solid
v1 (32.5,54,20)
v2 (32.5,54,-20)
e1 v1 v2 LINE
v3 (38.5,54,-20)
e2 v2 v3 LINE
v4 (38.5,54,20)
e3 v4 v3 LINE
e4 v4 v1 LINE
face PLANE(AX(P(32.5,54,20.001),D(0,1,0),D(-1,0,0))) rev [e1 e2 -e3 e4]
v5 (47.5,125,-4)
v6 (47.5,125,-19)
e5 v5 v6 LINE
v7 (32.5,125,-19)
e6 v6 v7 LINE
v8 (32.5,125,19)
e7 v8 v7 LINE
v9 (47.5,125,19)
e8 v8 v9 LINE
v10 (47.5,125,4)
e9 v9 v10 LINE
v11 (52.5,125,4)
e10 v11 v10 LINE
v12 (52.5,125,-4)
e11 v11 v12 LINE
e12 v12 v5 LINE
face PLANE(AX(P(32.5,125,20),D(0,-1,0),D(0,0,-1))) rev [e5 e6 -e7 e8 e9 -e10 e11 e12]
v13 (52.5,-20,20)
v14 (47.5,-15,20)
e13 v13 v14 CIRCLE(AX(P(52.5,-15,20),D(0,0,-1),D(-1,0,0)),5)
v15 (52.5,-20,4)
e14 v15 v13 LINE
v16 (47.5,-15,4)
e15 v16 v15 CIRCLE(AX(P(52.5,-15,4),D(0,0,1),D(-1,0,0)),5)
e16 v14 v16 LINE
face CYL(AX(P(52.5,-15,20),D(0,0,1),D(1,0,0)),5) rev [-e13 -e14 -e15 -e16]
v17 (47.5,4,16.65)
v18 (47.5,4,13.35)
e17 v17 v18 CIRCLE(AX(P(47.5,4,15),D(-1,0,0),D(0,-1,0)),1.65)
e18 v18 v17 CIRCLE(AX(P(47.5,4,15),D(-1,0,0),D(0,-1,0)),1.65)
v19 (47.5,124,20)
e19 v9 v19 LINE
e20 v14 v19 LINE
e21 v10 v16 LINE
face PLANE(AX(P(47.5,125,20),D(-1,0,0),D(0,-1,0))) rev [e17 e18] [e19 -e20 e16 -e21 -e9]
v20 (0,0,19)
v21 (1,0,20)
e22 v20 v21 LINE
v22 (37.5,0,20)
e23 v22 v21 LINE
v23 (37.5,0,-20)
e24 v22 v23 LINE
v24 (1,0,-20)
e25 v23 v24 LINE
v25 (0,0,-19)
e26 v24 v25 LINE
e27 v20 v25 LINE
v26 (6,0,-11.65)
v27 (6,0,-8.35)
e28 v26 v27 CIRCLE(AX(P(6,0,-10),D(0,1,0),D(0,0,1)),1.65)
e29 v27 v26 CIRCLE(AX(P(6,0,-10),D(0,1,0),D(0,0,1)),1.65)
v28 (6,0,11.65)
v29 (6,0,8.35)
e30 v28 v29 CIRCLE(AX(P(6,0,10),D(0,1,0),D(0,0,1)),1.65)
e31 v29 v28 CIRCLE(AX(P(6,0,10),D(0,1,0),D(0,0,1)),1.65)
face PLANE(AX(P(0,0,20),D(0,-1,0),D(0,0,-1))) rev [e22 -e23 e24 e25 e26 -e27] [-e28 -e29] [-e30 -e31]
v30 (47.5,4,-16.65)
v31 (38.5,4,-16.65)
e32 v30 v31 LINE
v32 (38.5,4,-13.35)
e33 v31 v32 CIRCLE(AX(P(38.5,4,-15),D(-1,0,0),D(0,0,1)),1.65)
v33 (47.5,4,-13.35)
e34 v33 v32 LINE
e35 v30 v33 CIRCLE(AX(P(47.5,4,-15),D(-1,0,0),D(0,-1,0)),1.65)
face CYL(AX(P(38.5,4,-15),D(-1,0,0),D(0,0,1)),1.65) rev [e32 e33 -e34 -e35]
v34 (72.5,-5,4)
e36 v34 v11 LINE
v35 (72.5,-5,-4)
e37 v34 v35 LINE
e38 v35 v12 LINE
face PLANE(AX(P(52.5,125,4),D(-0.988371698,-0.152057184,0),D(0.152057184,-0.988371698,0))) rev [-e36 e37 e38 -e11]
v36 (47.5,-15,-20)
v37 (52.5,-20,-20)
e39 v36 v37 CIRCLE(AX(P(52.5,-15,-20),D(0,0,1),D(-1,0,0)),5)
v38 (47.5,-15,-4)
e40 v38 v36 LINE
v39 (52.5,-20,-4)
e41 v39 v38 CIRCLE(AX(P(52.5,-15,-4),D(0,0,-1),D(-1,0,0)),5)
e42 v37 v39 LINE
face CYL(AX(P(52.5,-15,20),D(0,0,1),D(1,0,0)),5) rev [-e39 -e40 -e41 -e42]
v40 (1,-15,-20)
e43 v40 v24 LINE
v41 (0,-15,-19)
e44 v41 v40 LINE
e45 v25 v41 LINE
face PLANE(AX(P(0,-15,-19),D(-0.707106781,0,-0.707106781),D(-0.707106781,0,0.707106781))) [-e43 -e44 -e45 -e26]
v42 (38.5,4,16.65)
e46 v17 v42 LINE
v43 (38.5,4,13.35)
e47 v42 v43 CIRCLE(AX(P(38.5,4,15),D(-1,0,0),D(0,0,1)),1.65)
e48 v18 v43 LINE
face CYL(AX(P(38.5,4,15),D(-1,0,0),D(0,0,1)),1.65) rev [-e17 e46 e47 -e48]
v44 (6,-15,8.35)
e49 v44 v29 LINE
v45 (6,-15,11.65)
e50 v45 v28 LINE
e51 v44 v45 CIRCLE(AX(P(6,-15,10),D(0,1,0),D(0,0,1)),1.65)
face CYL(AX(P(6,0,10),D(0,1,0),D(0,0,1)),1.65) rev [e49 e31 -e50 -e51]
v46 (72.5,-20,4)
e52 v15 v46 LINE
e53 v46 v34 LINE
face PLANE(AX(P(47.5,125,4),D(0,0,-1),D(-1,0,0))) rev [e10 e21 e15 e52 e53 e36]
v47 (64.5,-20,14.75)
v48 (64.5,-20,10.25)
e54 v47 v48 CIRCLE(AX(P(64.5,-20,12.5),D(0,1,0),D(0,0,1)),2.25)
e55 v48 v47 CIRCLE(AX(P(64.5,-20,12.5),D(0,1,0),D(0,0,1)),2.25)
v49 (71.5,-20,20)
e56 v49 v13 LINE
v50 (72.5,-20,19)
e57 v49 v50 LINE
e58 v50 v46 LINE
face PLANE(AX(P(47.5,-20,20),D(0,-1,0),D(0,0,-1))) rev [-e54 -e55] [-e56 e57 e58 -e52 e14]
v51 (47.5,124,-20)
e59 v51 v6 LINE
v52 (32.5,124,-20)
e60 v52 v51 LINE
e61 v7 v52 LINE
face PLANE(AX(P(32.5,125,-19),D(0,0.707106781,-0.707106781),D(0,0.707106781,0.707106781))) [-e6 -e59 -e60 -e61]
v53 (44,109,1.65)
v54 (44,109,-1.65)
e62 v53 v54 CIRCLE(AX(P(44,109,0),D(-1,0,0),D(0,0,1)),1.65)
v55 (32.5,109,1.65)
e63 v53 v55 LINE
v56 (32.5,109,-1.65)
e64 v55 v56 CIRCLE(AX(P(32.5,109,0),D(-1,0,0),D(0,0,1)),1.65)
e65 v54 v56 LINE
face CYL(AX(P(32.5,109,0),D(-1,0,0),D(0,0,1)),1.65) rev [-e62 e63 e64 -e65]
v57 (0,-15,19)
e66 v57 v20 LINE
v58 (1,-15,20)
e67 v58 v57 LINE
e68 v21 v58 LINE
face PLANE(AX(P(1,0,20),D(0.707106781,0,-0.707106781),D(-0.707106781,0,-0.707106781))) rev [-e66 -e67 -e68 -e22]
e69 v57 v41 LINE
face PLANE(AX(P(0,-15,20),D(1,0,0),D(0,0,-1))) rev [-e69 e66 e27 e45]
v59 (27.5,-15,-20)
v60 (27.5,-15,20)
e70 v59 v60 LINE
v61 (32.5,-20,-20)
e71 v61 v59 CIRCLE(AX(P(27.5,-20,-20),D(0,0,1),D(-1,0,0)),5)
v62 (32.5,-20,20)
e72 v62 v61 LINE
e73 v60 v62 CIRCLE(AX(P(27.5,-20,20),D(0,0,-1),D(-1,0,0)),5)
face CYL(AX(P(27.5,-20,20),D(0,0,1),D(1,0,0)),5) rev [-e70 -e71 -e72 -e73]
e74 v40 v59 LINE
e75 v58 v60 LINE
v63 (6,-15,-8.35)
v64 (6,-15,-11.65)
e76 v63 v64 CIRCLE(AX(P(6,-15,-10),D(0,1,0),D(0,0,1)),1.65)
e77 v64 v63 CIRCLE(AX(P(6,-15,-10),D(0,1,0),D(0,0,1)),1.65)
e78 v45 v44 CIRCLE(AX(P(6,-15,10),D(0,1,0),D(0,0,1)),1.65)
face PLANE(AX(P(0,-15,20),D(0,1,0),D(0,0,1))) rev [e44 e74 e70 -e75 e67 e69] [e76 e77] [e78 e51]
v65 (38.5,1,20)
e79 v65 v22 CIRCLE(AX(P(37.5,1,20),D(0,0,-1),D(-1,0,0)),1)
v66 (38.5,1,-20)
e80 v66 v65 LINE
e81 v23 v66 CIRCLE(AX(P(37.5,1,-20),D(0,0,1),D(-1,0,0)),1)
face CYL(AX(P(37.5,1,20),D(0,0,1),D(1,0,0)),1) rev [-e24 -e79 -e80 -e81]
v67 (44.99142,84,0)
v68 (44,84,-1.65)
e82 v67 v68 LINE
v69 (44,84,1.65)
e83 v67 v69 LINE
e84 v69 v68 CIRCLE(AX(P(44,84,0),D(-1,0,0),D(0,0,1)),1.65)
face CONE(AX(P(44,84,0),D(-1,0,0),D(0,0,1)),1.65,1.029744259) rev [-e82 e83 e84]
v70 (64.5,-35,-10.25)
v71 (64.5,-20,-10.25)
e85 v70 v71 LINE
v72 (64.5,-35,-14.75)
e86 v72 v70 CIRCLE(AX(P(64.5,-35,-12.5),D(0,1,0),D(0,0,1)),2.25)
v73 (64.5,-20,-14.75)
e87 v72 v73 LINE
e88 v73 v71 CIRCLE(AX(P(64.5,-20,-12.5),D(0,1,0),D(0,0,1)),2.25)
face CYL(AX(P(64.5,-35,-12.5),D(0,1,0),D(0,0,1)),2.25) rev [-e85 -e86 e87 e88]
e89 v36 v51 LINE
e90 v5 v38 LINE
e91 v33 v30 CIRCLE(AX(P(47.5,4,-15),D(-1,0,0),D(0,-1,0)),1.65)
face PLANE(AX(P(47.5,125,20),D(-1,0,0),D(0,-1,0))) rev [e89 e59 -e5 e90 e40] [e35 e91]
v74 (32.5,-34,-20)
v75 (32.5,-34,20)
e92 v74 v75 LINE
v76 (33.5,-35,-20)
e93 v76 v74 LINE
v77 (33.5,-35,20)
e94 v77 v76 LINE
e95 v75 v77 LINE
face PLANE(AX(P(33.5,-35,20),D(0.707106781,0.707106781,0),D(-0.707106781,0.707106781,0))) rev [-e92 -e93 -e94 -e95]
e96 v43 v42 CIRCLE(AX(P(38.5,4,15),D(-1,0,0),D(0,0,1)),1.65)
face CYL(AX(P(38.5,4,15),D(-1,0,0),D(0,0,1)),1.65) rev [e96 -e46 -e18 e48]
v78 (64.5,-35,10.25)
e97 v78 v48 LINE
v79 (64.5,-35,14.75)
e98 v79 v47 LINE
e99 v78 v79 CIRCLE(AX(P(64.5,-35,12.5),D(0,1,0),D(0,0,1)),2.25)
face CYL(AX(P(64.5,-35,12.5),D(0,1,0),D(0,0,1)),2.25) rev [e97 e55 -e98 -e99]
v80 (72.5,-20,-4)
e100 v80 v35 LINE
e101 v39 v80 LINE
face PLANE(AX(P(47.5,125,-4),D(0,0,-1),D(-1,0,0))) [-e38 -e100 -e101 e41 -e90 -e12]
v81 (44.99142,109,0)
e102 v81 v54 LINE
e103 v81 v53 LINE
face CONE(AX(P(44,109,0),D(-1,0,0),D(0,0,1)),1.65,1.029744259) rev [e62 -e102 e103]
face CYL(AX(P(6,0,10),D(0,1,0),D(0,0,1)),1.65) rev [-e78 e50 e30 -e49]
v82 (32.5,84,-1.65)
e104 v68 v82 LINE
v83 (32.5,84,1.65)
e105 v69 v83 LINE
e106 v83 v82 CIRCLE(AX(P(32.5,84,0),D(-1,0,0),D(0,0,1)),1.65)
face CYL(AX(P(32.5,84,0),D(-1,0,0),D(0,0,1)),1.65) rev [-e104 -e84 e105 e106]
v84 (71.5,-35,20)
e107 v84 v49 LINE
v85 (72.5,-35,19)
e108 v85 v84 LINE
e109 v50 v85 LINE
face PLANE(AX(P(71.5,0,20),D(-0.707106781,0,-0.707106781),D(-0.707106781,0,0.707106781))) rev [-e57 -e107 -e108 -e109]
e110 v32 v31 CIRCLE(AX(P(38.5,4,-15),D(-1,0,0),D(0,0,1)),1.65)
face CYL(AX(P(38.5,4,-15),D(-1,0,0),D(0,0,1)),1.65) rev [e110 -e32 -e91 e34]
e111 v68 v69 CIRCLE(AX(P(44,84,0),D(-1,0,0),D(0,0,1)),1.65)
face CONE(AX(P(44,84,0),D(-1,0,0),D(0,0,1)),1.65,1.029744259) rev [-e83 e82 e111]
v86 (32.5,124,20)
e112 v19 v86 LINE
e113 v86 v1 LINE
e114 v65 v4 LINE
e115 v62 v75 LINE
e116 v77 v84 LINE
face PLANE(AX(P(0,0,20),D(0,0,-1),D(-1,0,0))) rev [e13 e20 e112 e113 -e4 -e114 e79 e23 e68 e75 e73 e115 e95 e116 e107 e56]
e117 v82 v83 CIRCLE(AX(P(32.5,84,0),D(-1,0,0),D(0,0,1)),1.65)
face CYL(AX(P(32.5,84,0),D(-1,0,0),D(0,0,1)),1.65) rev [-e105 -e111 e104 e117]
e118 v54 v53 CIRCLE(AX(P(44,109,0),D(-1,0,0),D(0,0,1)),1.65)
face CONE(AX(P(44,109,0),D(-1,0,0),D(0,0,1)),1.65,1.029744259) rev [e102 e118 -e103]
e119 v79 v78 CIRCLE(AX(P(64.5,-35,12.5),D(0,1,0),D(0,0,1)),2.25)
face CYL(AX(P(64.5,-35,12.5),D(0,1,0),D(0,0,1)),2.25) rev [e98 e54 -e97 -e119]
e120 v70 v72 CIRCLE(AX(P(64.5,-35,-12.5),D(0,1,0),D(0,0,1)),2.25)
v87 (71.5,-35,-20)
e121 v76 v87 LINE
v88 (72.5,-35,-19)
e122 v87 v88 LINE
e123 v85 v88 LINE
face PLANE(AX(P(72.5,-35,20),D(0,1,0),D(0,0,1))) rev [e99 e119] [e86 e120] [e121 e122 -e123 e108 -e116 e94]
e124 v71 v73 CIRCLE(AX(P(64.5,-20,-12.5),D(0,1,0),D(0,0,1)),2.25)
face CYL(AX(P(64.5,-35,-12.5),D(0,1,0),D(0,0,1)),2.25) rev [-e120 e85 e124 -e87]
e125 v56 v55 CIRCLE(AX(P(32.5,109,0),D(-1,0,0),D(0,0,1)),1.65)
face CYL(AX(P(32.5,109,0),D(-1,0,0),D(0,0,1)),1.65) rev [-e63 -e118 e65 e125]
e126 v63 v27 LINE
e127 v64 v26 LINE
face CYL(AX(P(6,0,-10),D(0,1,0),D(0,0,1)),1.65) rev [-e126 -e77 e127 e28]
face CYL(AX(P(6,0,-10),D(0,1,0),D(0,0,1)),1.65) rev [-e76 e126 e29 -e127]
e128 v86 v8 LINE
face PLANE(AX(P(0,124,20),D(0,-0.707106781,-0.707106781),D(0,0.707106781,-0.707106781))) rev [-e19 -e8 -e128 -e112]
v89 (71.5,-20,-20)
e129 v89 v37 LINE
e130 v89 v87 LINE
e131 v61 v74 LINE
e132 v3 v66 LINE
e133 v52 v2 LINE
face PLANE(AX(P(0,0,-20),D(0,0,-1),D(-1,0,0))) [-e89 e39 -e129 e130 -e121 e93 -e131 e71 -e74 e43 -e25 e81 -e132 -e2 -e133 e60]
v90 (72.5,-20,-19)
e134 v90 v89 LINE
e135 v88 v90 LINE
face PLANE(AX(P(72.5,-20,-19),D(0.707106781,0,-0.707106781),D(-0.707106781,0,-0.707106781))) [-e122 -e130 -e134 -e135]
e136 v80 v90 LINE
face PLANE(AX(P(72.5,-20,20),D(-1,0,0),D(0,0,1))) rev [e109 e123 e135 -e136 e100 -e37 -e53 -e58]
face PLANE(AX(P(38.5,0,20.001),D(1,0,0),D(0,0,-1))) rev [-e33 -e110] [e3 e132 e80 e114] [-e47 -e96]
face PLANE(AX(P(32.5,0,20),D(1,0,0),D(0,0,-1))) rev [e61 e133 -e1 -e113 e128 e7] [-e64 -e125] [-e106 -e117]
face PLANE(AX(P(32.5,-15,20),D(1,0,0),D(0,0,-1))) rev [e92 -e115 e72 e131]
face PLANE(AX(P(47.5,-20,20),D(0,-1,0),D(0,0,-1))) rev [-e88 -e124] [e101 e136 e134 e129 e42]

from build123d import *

# Parameters (mm, degrees)
BOSS_EXTRUDE1_DEPTH   = 20
BOSS_EXTRUDE2_DEPTH   = 4
SKETCH3_R             = 2.25
CUT_EXTRUDE2_DEPTH    = 164.343962239
M4_TAPPED_HOLE1_D     = 3.3
M4_TAPPED_HOLE2_D     = 3.3
M4_TAPPED_HOLE2_DEPTH = 11.5
M4_TAPPED_HOLE2_TIP   = 0.991420021
CUT_EXTRUDE3_REACH    = 151.937
SKETCH12_W            = 6
SKETCH12_H            = 54
M4_TAPPED_HOLE3_D     = 3.3
M4_TAPPED_HOLE3_DEPTH = 11.5
M4_TAPPED_HOLE3_TIP   = 0.991420021
CHAMFER1_SIZE         = 1
FILLET1_R             = 1
FILLET2_R             = 5


with BuildPart() as part:
    # Sketch1 → Boss-Extrude1 (new, symmetric)
    with BuildSketch(Plane.XY):
        Polygon((0, 0), (32.5, 0), (32.5, 125), (47.5, 125), (47.5, -20), (72.5, -20), (72.5, -35), (32.5, -35), (32.5, -15), (0, -15), align=None)
    extrude(amount=BOSS_EXTRUDE1_DEPTH, both=True)

    # Sketch2 → Boss-Extrude2 (add, symmetric)
    with BuildSketch(Plane.XY):
        Polygon((47.5, 125), (52.5, 125), (72.5, -5), (72.5, -20), (47.5, -20), align=None)
    extrude(amount=BOSS_EXTRUDE2_DEPTH, both=True)

    # Sketch3 → Cut-Extrude2 (cut, through all)
    with BuildSketch(Plane(origin=(0, -20, 0), x_dir=(1, 0, 0), z_dir=(0, 1, 0))):
        with Locations(Location((64.5, -12.5, 0), (0, 0, 270))):
            Circle(SKETCH3_R)
        with Locations(Location((64.5, 12.5, 0), (0, 0, 270))):
            Circle(SKETCH3_R)
    extrude(amount=-CUT_EXTRUDE2_DEPTH, mode=Mode.SUBTRACT)

    # M4 Tapped Hole1 (through all)
    with Locations(Plane(origin=(0, 0, 0), x_dir=(-1, 0, 0), z_dir=(0, 1, 0))):
        with Locations((-6, -10), (-6, 10)):
            Hole(M4_TAPPED_HOLE1_D / 2)

    # M4 Tapped Hole2
    with Locations(Plane(origin=(32.5, -167.050225356, 16.087508651), x_dir=(0, 0, 1), z_dir=(-1, 0, 0))):
        with Locations((-16.087508651, 276.050225356), (-16.087508651, 251.050225356)):
            Hole(M4_TAPPED_HOLE2_D / 2, depth=M4_TAPPED_HOLE2_DEPTH)
            with Locations((0, 0, -(M4_TAPPED_HOLE2_DEPTH + M4_TAPPED_HOLE2_TIP / 2))):  # 118° drill point
                Cone(0, M4_TAPPED_HOLE2_D / 2, M4_TAPPED_HOLE2_TIP, mode=Mode.SUBTRACT)

    # Sketch12 → Cut-Extrude3 (cut, up to next)
    with BuildSketch(Plane(origin=(0, 0, -20), x_dir=(-1, 0, 0), z_dir=(0, 0, -1)), mode=Mode.PRIVATE) as cut_extrude3_sk1:
        with Locations((-35.5, 27)):
            Rectangle(SKETCH12_W, SKETCH12_H)
    cut_extrude3_tool1 = extrude(cut_extrude3_sk1.sketch, amount=-CUT_EXTRUDE3_REACH, mode=Mode.PRIVATE) & part.part
    add(cut_extrude3_tool1.solids().sort_by_distance((35.5, 27, -20))[0], mode=Mode.SUBTRACT)

    # M4 Tapped Hole3
    with Locations(Plane.ZY.offset(-38.5)):
        with Locations((-15, 4), (15, 4)):
            Hole(M4_TAPPED_HOLE3_D / 2, depth=M4_TAPPED_HOLE3_DEPTH)
            with Locations((0, 0, -(M4_TAPPED_HOLE3_DEPTH + M4_TAPPED_HOLE3_TIP / 2))):  # 118° drill point
                Cone(0, M4_TAPPED_HOLE3_D / 2, M4_TAPPED_HOLE3_TIP, mode=Mode.SUBTRACT)

    # Chamfer1
    chamfer1_edges = [part.edges().sort_by_distance(p)[0] for p in [
        (40, 125, -20),
        (72.5, -27.5, -20),
        (0, -7.5, -20),
        (72.5, -27.5, 20),
        (32.5, -35, 0),
        (40, 125, 20),
        (0, -7.5, 20),
    ]]
    chamfer(chamfer1_edges, length=CHAMFER1_SIZE)

    # Fillet1
    fillet1_edges = [part.edges().sort_by_distance(p)[0] for p in [
        (38.5, 0, 0),
    ]]
    fillet(fillet1_edges, radius=FILLET1_R)

    # Fillet2
    fillet2_edges = [part.edges().sort_by_distance(p)[0] for p in [
        (47.5, -20, 12),
        (32.5, -15, 0),
        (47.5, -20, -12),
    ]]
    fillet(fillet2_edges, radius=FILLET2_R)


solid = part.part
